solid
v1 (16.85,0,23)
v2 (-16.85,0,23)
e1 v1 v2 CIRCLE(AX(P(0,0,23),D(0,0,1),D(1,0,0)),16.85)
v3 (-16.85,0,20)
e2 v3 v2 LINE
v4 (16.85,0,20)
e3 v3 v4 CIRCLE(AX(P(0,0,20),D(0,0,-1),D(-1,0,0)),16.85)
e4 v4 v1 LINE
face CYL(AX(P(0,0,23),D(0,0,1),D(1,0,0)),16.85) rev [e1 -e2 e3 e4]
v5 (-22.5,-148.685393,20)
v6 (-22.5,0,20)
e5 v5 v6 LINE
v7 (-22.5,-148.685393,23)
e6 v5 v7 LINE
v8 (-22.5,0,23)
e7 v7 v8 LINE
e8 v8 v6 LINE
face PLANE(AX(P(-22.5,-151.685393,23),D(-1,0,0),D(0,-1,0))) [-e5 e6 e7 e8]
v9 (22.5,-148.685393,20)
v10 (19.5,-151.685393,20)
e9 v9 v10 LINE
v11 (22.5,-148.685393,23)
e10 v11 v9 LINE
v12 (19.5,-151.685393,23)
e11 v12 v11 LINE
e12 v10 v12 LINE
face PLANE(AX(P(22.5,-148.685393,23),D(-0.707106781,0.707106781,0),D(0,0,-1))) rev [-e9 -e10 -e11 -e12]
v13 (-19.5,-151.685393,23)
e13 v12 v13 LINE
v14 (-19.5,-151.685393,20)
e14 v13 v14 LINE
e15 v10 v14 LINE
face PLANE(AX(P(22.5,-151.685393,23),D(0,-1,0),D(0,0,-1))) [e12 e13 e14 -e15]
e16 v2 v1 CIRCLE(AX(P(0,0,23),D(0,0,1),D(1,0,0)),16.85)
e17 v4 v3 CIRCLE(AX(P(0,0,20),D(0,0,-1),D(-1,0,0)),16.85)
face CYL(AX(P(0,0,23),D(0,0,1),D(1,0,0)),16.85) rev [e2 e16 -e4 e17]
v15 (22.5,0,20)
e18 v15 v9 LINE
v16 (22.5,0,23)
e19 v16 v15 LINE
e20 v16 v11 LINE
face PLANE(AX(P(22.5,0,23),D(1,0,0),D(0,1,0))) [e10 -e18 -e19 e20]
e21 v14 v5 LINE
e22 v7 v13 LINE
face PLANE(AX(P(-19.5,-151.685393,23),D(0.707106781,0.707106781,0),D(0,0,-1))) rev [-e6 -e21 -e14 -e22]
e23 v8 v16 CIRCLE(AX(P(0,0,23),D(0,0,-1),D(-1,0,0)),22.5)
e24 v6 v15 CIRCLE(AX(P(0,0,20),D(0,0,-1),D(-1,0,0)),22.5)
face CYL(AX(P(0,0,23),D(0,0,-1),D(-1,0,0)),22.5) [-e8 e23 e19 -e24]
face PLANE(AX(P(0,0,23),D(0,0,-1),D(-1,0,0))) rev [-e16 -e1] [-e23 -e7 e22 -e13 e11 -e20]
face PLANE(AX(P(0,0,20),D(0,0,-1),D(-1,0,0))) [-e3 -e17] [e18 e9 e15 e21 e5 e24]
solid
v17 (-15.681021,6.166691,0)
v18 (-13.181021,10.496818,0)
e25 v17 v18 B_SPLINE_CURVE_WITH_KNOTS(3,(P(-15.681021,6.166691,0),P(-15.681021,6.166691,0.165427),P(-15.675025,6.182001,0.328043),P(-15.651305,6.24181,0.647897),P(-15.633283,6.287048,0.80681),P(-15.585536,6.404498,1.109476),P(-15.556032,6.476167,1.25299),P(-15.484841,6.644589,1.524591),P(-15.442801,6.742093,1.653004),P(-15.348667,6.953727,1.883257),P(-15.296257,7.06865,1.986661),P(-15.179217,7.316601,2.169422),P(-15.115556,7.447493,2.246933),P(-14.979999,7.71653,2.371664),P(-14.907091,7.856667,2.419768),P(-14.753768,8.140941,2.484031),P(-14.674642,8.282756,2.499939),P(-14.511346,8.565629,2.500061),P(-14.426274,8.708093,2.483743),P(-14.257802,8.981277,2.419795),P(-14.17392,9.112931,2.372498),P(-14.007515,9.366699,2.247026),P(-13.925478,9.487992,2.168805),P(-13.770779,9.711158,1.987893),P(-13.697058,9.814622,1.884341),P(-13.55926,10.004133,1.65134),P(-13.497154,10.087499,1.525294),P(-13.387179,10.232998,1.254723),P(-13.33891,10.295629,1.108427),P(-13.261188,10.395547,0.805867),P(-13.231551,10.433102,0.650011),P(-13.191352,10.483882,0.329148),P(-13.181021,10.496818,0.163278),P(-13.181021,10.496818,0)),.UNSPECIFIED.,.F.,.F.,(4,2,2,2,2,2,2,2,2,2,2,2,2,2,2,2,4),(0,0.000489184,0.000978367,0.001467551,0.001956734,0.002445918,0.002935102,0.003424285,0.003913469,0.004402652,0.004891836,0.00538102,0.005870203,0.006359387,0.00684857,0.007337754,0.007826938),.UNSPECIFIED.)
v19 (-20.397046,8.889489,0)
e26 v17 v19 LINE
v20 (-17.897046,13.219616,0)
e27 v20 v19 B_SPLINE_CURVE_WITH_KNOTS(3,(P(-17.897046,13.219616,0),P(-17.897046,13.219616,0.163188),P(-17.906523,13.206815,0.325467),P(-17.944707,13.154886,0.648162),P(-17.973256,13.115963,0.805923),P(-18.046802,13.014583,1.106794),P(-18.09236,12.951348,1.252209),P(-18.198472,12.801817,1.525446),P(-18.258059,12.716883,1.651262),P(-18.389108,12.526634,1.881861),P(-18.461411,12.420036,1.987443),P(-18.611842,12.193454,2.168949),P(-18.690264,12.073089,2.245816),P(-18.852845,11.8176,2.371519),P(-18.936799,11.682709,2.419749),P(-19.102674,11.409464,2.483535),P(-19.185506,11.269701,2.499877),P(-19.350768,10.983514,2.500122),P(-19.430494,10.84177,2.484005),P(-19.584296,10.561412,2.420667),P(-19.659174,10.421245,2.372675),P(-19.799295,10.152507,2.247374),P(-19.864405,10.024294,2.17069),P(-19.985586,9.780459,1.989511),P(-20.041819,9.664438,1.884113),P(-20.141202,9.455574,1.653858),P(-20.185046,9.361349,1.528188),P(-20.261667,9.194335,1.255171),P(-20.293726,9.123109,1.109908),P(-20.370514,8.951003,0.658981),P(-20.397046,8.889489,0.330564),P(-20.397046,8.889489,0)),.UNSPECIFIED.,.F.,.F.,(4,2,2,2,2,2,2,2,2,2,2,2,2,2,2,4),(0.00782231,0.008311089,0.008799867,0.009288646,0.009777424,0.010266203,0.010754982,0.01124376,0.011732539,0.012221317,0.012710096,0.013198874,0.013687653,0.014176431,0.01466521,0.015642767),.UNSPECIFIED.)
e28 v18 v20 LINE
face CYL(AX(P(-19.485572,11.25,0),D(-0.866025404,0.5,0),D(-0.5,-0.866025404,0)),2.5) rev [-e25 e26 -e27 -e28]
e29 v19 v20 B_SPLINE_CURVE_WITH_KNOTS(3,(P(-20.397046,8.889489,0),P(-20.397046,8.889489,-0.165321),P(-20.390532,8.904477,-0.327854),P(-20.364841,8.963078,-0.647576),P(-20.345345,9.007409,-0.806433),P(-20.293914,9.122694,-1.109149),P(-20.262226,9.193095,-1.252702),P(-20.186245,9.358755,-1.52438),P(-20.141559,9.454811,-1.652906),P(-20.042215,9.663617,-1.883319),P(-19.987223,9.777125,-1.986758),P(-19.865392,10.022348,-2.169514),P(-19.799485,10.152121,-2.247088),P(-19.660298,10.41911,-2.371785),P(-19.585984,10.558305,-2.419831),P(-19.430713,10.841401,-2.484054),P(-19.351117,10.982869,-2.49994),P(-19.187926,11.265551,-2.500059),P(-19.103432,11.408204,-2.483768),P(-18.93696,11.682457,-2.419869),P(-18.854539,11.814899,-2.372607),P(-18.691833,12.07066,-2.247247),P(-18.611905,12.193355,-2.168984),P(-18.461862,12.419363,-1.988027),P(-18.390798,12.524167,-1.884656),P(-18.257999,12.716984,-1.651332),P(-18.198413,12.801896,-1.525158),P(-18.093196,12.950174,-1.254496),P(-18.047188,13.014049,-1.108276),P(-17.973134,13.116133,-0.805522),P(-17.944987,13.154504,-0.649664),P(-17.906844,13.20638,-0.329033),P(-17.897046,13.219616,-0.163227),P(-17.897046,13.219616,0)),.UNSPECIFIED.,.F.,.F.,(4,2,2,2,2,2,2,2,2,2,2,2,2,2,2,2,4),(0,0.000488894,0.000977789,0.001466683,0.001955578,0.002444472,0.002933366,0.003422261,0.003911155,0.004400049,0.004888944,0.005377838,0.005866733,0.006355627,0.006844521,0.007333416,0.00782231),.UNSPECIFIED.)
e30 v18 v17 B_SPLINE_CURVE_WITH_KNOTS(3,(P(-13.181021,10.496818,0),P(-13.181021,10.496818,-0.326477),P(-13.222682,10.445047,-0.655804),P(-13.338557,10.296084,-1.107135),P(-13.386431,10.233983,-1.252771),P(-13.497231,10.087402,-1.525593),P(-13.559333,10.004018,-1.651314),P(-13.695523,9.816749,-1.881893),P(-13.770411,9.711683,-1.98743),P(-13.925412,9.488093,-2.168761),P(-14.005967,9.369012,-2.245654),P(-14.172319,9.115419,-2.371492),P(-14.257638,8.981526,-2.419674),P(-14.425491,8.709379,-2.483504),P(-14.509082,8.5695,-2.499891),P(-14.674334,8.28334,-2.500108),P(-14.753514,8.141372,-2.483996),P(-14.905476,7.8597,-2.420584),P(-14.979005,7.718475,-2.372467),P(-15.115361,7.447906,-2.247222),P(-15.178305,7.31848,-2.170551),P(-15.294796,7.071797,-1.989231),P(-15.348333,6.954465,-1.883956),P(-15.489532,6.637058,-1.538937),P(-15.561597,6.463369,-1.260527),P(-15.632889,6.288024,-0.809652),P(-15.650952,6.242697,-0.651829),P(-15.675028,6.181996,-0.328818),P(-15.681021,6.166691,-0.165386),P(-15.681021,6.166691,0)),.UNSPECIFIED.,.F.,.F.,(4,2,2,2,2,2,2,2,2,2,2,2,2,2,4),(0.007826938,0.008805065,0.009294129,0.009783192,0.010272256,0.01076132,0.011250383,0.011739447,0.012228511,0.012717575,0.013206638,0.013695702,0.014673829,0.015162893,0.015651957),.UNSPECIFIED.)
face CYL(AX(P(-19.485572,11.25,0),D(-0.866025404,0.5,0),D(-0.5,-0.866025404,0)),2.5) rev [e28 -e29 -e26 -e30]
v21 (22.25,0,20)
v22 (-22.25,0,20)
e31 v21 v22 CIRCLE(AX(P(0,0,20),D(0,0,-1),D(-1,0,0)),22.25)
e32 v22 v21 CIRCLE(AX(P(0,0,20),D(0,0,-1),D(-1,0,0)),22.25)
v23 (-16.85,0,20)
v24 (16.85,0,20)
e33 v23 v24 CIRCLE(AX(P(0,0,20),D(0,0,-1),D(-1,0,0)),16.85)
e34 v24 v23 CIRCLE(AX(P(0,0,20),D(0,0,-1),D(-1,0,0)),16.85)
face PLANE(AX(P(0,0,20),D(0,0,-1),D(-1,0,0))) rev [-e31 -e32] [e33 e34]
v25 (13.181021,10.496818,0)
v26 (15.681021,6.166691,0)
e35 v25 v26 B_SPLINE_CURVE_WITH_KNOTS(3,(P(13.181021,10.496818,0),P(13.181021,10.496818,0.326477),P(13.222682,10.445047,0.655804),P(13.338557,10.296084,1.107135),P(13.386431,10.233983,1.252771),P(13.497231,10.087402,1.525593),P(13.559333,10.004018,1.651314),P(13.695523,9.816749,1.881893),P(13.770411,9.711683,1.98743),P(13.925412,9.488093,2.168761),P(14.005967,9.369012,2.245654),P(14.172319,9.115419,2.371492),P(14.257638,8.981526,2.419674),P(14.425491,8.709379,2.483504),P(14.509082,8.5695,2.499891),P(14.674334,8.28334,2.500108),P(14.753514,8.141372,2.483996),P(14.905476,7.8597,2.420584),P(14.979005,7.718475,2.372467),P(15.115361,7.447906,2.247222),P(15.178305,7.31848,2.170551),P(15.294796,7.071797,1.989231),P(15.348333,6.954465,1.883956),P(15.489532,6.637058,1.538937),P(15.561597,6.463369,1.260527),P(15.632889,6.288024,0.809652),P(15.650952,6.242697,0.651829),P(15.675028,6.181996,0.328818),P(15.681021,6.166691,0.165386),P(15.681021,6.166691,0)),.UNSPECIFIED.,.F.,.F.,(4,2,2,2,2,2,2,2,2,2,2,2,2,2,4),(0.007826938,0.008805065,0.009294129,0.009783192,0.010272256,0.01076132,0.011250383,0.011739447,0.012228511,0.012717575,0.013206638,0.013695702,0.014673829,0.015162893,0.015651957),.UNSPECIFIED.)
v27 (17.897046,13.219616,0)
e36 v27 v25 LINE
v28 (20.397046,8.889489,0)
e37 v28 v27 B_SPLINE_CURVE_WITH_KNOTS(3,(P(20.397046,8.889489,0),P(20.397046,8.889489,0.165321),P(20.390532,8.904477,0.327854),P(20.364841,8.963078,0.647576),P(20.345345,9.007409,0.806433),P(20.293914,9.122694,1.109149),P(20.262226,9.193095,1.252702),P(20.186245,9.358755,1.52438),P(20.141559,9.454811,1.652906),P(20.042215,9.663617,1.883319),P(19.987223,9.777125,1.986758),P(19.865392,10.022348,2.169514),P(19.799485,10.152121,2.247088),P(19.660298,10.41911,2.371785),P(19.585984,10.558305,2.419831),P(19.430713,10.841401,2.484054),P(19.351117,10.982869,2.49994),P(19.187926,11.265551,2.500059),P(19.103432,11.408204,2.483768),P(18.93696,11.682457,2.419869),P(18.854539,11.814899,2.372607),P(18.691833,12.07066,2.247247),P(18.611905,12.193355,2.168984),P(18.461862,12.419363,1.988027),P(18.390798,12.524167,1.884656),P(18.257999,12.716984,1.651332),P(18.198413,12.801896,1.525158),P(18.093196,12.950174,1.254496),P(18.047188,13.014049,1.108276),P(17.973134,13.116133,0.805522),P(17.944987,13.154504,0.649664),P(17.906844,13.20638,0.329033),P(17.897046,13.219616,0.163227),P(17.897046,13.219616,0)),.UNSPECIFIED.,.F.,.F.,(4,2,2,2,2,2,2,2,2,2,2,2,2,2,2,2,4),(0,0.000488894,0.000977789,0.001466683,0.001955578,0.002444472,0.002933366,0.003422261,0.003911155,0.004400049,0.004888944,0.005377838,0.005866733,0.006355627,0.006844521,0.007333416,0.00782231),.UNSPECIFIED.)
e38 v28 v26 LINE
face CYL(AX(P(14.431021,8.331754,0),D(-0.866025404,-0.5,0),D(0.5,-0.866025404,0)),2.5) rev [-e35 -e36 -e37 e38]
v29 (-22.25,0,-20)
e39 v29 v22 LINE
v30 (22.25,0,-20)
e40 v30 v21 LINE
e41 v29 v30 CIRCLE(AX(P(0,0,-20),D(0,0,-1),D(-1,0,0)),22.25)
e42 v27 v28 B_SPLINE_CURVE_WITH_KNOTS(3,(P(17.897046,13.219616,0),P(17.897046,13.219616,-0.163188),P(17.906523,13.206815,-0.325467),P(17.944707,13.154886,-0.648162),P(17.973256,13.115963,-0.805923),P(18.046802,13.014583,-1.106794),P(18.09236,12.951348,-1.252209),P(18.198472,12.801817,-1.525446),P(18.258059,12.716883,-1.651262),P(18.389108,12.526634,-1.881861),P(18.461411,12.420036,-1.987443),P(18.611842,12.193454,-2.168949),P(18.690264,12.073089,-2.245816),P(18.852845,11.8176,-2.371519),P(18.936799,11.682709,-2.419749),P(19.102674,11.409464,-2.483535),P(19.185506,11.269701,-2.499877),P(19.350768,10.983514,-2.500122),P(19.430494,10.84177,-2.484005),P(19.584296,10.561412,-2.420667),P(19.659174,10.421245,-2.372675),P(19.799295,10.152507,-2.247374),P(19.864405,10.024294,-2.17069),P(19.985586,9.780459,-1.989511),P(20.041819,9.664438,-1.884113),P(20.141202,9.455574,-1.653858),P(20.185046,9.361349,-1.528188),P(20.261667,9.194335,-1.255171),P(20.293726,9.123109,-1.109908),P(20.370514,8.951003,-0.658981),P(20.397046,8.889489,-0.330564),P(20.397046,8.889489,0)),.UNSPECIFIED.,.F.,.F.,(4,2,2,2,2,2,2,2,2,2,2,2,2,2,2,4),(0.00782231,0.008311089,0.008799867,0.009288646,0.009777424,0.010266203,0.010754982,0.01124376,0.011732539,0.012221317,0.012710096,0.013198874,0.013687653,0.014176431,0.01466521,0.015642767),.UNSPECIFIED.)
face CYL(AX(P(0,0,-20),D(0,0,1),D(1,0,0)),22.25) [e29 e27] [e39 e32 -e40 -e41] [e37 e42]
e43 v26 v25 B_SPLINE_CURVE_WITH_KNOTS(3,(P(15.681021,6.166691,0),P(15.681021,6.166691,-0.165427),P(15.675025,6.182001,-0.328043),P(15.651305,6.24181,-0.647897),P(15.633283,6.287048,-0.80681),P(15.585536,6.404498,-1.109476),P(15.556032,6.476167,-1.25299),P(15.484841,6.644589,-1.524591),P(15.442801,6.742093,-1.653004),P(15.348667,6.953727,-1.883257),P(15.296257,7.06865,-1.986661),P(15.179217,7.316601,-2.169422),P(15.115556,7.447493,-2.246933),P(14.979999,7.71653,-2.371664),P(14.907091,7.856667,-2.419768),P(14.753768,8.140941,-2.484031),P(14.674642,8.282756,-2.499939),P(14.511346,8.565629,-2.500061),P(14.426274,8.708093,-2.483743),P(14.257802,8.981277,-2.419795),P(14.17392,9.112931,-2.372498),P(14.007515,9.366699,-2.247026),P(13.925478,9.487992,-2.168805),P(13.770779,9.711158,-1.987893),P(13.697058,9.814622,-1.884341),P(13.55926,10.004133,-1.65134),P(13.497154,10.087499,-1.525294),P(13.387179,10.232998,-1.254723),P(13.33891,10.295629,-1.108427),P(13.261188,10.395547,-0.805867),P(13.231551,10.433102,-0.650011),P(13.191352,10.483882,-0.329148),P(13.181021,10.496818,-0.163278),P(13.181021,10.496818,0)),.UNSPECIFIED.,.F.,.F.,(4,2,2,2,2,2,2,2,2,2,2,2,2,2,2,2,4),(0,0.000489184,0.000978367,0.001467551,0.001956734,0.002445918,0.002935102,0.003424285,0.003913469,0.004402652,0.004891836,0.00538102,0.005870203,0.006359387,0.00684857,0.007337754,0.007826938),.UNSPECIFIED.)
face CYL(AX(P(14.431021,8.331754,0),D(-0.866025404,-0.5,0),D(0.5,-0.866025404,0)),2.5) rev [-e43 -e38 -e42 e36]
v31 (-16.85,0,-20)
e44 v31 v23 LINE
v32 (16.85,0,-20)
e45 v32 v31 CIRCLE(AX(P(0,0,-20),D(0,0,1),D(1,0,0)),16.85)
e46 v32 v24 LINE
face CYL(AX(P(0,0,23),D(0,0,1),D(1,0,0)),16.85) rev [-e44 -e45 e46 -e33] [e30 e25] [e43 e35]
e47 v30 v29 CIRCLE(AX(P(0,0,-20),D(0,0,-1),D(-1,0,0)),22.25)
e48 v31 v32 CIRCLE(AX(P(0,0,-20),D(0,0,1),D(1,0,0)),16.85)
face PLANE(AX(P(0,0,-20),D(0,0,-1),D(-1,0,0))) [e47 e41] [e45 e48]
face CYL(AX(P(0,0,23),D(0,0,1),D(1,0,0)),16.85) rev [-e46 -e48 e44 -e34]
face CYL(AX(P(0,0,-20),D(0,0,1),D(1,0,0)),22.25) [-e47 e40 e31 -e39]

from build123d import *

# Parameters (mm, degrees)
EXTRUDE_1_DEPTH = 3
SKETCH_2_R      = 22.25
EXTRUDE_2_DEPTH = 40
SKETCH_3_W      = 16.85
SKETCH_3_H      = 43
SKETCH_5_W      = 2.5
SKETCH_5_H      = 22.5
SKETCH_6_W      = 2.5
SKETCH_6_H      = 14.072063551
CHAMFER_1_SIZE  = 3


with BuildPart() as part:
    # 草图1 → 凸台-拉伸1 (new body)
    with BuildSketch(Plane(origin=(0, 0, 20), x_dir=(-1, 0, 0), z_dir=(0, 0, -1))):
        with BuildLine():
            Line((-22.5, 0), (-22.5, -151.685393258))
            Line((-22.5, -151.685393258), (22.5, -151.685393258))
            Line((22.5, -151.685393258), (22.5, 0))
            ThreePointArc((22.5, 0), (0, 22.5), (-22.5, 0))
        make_face()
    extrude(amount=-EXTRUDE_1_DEPTH)


with BuildPart() as body_2:
    # 草图2 → 凸台-拉伸2 (new body)
    with BuildSketch(Plane(origin=(0, 0, 20), x_dir=(-1, 0, 0), z_dir=(0, 0, -1))):
        Circle(SKETCH_2_R)
    extrude(amount=EXTRUDE_2_DEPTH)


with BuildPart() as hole_wizard_m30_1_tool:
    # 草图3 → M30 间隙孔1 (revolve)
    with BuildSketch(Plane(origin=(0, 0, 23), x_dir=(0, -1, 0), z_dir=(1, 0, 0))):
        with Locations((8.425, 21.5)):
            Rectangle(SKETCH_3_W, SKETCH_3_H)
    revolve(axis=Axis((0, 0, 29.35), (0, 0, -1)))


with BuildPart() as part_1:
    add(part.part)

    # M30 间隙孔1: cut by hole_wizard_m30_1_tool
    add(hole_wizard_m30_1_tool.part, mode=Mode.SUBTRACT)

    # 倒角1
    chamfer_1_edges = [part_1.edges().sort_by_distance(p)[0] for p in [
        (-22.5, -151.685393258, 21.5),
        (22.5, -151.685393258, 21.5),
    ]]
    chamfer(chamfer_1_edges, length=CHAMFER_1_SIZE)


with BuildPart() as body_2_1:
    add(body_2.part)

    # M30 间隙孔1: cut by hole_wizard_m30_1_tool
    add(hole_wizard_m30_1_tool.part, mode=Mode.SUBTRACT)

    # 草图5 → Ø5.0 (5) 直径孔1 (revolve, cut)
    with BuildSketch(Plane(origin=(-19.485571585, 11.25, 0), x_dir=(-0.4999999999999359, -0.8660254037844758, 0), z_dir=(0, 0, 1))):
        with Locations((1.25, 11.25)):
            Rectangle(SKETCH_5_W, SKETCH_5_H)
    revolve(axis=Axis((-24.984832899, 14.425, 0), (0.8660254037844757, -0.4999999999999359, 0)), mode=Mode.SUBTRACT)

    # 草图6 → Ø5.0 (5) 直径孔2 (revolve, cut)
    with BuildSketch(Plane(origin=(14.431021274, 8.331754017, 0), x_dir=(0.5000000000000044, -0.8660254037844362, 0), z_dir=(0, 0, 1))):
        with Locations((1.25, 7.036031776)):
            Rectangle(SKETCH_6_W, SKETCH_6_H)
    revolve(axis=Axis((8.93175996, 5.156754017, 0), (0.866025403784436, 0.5000000000000044, 0)), mode=Mode.SUBTRACT)


solid = Compound([part_1.part, body_2_1.part])
